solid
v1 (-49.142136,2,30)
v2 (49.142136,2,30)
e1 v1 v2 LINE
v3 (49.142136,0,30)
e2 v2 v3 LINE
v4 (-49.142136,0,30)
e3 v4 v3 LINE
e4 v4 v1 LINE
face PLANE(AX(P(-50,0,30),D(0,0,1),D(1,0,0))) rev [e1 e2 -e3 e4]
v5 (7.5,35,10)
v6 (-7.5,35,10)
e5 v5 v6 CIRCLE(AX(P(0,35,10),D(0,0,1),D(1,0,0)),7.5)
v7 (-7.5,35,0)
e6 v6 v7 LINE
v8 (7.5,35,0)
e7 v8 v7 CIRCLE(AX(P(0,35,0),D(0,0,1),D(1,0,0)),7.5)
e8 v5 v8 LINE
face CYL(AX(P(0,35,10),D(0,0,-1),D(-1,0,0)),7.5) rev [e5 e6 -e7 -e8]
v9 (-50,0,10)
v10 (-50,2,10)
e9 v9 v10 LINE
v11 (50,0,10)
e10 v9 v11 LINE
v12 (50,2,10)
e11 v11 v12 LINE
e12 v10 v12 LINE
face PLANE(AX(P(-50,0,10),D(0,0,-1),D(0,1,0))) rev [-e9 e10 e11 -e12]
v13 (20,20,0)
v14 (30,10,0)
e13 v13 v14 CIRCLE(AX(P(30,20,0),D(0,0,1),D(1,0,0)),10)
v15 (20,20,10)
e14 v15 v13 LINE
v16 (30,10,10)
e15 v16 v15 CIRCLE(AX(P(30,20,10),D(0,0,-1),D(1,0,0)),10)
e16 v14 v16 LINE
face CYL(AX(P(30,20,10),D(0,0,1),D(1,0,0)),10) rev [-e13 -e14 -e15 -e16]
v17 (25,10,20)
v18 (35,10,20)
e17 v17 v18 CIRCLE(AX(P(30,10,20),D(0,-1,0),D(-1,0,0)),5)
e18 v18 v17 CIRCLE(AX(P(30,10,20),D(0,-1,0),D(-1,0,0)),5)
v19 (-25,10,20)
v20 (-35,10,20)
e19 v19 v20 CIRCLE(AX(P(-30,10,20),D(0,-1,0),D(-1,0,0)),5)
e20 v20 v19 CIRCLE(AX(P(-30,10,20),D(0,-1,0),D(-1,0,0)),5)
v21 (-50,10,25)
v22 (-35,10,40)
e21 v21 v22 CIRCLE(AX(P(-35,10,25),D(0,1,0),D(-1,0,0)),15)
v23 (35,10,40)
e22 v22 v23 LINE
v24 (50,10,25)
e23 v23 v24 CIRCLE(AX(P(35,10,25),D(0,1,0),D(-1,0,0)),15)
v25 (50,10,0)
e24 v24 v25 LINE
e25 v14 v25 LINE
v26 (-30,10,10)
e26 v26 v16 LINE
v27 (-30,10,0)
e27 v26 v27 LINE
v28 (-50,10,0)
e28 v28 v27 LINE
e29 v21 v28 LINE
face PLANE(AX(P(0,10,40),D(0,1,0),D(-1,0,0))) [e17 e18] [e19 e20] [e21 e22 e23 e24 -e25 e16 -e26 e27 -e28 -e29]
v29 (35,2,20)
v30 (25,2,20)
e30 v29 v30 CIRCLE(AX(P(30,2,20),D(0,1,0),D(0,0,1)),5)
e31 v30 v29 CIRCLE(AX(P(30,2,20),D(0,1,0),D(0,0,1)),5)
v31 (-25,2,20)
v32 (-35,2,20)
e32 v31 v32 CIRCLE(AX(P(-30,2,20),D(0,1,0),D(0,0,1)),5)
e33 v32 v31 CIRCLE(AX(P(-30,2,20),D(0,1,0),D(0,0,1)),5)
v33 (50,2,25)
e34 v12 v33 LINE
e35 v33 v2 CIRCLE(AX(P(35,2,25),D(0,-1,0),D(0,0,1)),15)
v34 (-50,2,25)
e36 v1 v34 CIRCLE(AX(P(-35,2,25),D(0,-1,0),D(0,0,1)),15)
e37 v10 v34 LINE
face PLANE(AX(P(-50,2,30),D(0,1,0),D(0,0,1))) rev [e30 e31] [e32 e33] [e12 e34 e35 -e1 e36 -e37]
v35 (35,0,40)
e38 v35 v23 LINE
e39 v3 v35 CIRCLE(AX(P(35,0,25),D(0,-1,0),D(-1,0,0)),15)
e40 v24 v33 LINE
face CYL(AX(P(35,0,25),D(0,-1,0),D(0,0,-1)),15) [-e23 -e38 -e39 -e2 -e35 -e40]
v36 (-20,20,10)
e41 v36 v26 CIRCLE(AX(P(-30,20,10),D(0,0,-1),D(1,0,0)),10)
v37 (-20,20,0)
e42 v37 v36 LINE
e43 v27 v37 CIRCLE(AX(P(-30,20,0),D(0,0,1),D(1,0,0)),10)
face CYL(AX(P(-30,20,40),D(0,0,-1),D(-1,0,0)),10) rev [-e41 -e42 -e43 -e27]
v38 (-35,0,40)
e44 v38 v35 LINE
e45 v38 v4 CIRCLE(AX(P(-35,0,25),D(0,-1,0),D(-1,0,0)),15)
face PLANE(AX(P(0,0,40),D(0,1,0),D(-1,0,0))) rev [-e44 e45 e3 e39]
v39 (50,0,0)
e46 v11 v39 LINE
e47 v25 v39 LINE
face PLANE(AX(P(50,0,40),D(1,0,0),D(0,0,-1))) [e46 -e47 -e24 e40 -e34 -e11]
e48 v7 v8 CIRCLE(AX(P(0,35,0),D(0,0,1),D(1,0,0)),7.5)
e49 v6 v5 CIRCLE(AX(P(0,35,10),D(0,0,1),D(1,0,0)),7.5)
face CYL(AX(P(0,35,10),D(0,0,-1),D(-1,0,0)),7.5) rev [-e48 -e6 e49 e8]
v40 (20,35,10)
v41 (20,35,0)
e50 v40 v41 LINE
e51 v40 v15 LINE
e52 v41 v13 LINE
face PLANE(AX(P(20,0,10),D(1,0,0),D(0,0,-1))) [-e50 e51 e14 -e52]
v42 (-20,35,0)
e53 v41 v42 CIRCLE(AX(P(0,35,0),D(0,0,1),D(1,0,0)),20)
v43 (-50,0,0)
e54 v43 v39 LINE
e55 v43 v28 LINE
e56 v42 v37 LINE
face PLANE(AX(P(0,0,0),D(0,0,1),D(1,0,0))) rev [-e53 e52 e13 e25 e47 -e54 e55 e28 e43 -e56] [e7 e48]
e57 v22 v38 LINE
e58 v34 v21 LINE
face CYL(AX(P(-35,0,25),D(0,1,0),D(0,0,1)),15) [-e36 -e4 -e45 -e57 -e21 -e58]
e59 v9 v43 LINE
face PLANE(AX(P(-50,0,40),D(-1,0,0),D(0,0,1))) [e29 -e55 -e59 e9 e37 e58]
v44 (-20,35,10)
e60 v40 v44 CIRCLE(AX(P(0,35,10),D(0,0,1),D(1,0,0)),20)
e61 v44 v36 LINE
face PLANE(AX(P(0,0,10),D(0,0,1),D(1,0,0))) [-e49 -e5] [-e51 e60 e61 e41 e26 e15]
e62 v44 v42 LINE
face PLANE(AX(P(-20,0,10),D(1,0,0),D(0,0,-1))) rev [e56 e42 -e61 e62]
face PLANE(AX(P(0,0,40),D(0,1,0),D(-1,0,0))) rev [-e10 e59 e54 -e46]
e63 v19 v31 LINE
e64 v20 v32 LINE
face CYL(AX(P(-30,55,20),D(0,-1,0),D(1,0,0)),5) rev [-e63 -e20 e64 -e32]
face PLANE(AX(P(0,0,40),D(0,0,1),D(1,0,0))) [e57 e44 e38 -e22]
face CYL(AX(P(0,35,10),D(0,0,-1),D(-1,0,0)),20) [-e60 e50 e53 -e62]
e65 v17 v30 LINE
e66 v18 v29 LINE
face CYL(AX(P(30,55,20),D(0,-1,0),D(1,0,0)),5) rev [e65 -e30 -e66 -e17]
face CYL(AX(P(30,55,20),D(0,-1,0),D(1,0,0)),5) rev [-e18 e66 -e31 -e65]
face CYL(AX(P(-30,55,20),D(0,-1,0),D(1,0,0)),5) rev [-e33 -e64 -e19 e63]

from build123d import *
from OCP.BRepFilletAPI import BRepFilletAPI_MakeFillet

# Parameters (mm, degrees)
BASE_AND_EAR_PROFILE_SKETCH_W       = 100
BASE_AND_EAR_PROFILE_SKETCH_H       = 10
BASE_PLATE_DEPTH                    = 40
SKETCH1_3_R                         = 20
SKETCH1_3_R_2                       = 7.5
CLEVIS_EAR_DEPTH                    = 10
MOUNTING_HOLES_2X_REACH             = 80.262
MOUNTING_HOLES_SKETCH_R             = 5
MOUNTING_HOLES_2X_DIRECTION_2_DEPTH = 79.262379212
CORNER_AND_EAR_FILLETS_R1           = 10
CORNER_AND_EAR_FILLETS_R2           = 15
BOTTOM_GROOVE_DEPTH                 = 85.409715081
BOTTOM_GROOVE_DEPTH_BACK            = 85.409715081
BOTTOM_GROOVE_SKETCH_W              = 20
BOTTOM_GROOVE_SKETCH_H              = 2


with BuildPart() as part:
    # Base and Ear Profile Sketch → Base Plate (new body)
    with BuildSketch(Plane.XY):
        with Locations((0, 5)):
            Rectangle(BASE_AND_EAR_PROFILE_SKETCH_W, BASE_AND_EAR_PROFILE_SKETCH_H)
    extrude(amount=BASE_PLATE_DEPTH)

    # Sketch1_3 → Clevis Ear (add)
    # profile 1 of 2: a face of its own
    with BuildSketch(Plane.XY):
        with BuildLine():
            Line((-20, 35), (-20, 10))
            Line((-20, 10), (20, 10))
            Line((20, 10), (20, 35))
            ThreePointArc((20, 35), (0, 15), (-20, 35))
        make_face()
    # profile 2 of 2: a face of its own
    with BuildSketch(Plane.XY):
        with Locations((0, 35)):
            Circle(SKETCH1_3_R)
        with Locations((0, 35)):
            Circle(SKETCH1_3_R_2, mode=Mode.SUBTRACT)
    extrude(amount=CLEVIS_EAR_DEPTH)

    # Mounting Holes Sketch → Mounting Holes 2x (cut, up to next)
    with BuildSketch(Plane(origin=(0, 10, 0), x_dir=(1, 0, 0), z_dir=(0, 1, 0)), mode=Mode.PRIVATE) as mounting_holes_2x_sk1:
        with Locations(Location((30, -20, 0), (0, 0, 180))):
            Circle(MOUNTING_HOLES_SKETCH_R)
    mounting_holes_2x_tool1 = extrude(mounting_holes_2x_sk1.sketch, amount=-MOUNTING_HOLES_2X_REACH, mode=Mode.PRIVATE) & part.part
    # Mounting Holes Sketch → Mounting Holes 2x (cut, up to next)
    with BuildSketch(Plane(origin=(0, 10, 0), x_dir=(1, 0, 0), z_dir=(0, 1, 0)), mode=Mode.PRIVATE) as mounting_holes_2x_sk2:
        with Locations(Location((-30, -20, 0), (0, 0, 180))):
            Circle(MOUNTING_HOLES_SKETCH_R)
    mounting_holes_2x_tool2 = extrude(mounting_holes_2x_sk2.sketch, amount=-MOUNTING_HOLES_2X_REACH, mode=Mode.PRIVATE) & part.part
    add(mounting_holes_2x_tool1.solids().sort_by_distance((30, 10, 20))[0], mode=Mode.SUBTRACT)
    add(mounting_holes_2x_tool2.solids().sort_by_distance((-30, 10, 20))[0], mode=Mode.SUBTRACT)

    # Mounting Holes Sketch → Mounting Holes 2x direction 2 (cut)
    with BuildSketch(Plane(origin=(0, 10, 0), x_dir=(1, 0, 0), z_dir=(0, 1, 0))):
        with Locations(Location((30, -20, 0), (0, 0, 180))):
            Circle(MOUNTING_HOLES_SKETCH_R)
        with Locations(Location((-30, -20, 0), (0, 0, 180))):
            Circle(MOUNTING_HOLES_SKETCH_R)
    extrude(amount=MOUNTING_HOLES_2X_DIRECTION_2_DEPTH, mode=Mode.SUBTRACT)

    # Corner and Ear Fillets: one fillet with a radius per group of edges: ONE call of the kernel's fillet builder (fillet() takes one radius for all edges)
    corner_and_ear_fillets_edges_1 = [part.edges().sort_by_distance(p)[0] for p in [
        (20, 10, 5),
        (-20, 10, 5),
    ]]
    corner_and_ear_fillets_edges_2 = [part.edges().sort_by_distance(p)[0] for p in [
        (-50, 5, 40),
        (50, 5, 40),
    ]]
    corner_and_ear_fillets = BRepFilletAPI_MakeFillet(part.part.solid().wrapped)
    for e in corner_and_ear_fillets_edges_1:
        corner_and_ear_fillets.Add(CORNER_AND_EAR_FILLETS_R1, e.wrapped)
    for e in corner_and_ear_fillets_edges_2:
        corner_and_ear_fillets.Add(CORNER_AND_EAR_FILLETS_R2, e.wrapped)
    add(Compound.cast(corner_and_ear_fillets.Shape()), mode=Mode.REPLACE)

    # Bottom Groove Sketch → Bottom Groove (cut, two sides: drawn at the far end of the back side and taken through both)
    with BuildSketch(Plane(origin=(0, 0, 0), x_dir=(0, 0, -1), z_dir=(1, 0, 0)).offset(-BOTTOM_GROOVE_DEPTH_BACK)):
        with Locations((-20, 1)):
            Rectangle(BOTTOM_GROOVE_SKETCH_W, BOTTOM_GROOVE_SKETCH_H)
    extrude(amount=BOTTOM_GROOVE_DEPTH + BOTTOM_GROOVE_DEPTH_BACK, mode=Mode.SUBTRACT)


solid = part.part
